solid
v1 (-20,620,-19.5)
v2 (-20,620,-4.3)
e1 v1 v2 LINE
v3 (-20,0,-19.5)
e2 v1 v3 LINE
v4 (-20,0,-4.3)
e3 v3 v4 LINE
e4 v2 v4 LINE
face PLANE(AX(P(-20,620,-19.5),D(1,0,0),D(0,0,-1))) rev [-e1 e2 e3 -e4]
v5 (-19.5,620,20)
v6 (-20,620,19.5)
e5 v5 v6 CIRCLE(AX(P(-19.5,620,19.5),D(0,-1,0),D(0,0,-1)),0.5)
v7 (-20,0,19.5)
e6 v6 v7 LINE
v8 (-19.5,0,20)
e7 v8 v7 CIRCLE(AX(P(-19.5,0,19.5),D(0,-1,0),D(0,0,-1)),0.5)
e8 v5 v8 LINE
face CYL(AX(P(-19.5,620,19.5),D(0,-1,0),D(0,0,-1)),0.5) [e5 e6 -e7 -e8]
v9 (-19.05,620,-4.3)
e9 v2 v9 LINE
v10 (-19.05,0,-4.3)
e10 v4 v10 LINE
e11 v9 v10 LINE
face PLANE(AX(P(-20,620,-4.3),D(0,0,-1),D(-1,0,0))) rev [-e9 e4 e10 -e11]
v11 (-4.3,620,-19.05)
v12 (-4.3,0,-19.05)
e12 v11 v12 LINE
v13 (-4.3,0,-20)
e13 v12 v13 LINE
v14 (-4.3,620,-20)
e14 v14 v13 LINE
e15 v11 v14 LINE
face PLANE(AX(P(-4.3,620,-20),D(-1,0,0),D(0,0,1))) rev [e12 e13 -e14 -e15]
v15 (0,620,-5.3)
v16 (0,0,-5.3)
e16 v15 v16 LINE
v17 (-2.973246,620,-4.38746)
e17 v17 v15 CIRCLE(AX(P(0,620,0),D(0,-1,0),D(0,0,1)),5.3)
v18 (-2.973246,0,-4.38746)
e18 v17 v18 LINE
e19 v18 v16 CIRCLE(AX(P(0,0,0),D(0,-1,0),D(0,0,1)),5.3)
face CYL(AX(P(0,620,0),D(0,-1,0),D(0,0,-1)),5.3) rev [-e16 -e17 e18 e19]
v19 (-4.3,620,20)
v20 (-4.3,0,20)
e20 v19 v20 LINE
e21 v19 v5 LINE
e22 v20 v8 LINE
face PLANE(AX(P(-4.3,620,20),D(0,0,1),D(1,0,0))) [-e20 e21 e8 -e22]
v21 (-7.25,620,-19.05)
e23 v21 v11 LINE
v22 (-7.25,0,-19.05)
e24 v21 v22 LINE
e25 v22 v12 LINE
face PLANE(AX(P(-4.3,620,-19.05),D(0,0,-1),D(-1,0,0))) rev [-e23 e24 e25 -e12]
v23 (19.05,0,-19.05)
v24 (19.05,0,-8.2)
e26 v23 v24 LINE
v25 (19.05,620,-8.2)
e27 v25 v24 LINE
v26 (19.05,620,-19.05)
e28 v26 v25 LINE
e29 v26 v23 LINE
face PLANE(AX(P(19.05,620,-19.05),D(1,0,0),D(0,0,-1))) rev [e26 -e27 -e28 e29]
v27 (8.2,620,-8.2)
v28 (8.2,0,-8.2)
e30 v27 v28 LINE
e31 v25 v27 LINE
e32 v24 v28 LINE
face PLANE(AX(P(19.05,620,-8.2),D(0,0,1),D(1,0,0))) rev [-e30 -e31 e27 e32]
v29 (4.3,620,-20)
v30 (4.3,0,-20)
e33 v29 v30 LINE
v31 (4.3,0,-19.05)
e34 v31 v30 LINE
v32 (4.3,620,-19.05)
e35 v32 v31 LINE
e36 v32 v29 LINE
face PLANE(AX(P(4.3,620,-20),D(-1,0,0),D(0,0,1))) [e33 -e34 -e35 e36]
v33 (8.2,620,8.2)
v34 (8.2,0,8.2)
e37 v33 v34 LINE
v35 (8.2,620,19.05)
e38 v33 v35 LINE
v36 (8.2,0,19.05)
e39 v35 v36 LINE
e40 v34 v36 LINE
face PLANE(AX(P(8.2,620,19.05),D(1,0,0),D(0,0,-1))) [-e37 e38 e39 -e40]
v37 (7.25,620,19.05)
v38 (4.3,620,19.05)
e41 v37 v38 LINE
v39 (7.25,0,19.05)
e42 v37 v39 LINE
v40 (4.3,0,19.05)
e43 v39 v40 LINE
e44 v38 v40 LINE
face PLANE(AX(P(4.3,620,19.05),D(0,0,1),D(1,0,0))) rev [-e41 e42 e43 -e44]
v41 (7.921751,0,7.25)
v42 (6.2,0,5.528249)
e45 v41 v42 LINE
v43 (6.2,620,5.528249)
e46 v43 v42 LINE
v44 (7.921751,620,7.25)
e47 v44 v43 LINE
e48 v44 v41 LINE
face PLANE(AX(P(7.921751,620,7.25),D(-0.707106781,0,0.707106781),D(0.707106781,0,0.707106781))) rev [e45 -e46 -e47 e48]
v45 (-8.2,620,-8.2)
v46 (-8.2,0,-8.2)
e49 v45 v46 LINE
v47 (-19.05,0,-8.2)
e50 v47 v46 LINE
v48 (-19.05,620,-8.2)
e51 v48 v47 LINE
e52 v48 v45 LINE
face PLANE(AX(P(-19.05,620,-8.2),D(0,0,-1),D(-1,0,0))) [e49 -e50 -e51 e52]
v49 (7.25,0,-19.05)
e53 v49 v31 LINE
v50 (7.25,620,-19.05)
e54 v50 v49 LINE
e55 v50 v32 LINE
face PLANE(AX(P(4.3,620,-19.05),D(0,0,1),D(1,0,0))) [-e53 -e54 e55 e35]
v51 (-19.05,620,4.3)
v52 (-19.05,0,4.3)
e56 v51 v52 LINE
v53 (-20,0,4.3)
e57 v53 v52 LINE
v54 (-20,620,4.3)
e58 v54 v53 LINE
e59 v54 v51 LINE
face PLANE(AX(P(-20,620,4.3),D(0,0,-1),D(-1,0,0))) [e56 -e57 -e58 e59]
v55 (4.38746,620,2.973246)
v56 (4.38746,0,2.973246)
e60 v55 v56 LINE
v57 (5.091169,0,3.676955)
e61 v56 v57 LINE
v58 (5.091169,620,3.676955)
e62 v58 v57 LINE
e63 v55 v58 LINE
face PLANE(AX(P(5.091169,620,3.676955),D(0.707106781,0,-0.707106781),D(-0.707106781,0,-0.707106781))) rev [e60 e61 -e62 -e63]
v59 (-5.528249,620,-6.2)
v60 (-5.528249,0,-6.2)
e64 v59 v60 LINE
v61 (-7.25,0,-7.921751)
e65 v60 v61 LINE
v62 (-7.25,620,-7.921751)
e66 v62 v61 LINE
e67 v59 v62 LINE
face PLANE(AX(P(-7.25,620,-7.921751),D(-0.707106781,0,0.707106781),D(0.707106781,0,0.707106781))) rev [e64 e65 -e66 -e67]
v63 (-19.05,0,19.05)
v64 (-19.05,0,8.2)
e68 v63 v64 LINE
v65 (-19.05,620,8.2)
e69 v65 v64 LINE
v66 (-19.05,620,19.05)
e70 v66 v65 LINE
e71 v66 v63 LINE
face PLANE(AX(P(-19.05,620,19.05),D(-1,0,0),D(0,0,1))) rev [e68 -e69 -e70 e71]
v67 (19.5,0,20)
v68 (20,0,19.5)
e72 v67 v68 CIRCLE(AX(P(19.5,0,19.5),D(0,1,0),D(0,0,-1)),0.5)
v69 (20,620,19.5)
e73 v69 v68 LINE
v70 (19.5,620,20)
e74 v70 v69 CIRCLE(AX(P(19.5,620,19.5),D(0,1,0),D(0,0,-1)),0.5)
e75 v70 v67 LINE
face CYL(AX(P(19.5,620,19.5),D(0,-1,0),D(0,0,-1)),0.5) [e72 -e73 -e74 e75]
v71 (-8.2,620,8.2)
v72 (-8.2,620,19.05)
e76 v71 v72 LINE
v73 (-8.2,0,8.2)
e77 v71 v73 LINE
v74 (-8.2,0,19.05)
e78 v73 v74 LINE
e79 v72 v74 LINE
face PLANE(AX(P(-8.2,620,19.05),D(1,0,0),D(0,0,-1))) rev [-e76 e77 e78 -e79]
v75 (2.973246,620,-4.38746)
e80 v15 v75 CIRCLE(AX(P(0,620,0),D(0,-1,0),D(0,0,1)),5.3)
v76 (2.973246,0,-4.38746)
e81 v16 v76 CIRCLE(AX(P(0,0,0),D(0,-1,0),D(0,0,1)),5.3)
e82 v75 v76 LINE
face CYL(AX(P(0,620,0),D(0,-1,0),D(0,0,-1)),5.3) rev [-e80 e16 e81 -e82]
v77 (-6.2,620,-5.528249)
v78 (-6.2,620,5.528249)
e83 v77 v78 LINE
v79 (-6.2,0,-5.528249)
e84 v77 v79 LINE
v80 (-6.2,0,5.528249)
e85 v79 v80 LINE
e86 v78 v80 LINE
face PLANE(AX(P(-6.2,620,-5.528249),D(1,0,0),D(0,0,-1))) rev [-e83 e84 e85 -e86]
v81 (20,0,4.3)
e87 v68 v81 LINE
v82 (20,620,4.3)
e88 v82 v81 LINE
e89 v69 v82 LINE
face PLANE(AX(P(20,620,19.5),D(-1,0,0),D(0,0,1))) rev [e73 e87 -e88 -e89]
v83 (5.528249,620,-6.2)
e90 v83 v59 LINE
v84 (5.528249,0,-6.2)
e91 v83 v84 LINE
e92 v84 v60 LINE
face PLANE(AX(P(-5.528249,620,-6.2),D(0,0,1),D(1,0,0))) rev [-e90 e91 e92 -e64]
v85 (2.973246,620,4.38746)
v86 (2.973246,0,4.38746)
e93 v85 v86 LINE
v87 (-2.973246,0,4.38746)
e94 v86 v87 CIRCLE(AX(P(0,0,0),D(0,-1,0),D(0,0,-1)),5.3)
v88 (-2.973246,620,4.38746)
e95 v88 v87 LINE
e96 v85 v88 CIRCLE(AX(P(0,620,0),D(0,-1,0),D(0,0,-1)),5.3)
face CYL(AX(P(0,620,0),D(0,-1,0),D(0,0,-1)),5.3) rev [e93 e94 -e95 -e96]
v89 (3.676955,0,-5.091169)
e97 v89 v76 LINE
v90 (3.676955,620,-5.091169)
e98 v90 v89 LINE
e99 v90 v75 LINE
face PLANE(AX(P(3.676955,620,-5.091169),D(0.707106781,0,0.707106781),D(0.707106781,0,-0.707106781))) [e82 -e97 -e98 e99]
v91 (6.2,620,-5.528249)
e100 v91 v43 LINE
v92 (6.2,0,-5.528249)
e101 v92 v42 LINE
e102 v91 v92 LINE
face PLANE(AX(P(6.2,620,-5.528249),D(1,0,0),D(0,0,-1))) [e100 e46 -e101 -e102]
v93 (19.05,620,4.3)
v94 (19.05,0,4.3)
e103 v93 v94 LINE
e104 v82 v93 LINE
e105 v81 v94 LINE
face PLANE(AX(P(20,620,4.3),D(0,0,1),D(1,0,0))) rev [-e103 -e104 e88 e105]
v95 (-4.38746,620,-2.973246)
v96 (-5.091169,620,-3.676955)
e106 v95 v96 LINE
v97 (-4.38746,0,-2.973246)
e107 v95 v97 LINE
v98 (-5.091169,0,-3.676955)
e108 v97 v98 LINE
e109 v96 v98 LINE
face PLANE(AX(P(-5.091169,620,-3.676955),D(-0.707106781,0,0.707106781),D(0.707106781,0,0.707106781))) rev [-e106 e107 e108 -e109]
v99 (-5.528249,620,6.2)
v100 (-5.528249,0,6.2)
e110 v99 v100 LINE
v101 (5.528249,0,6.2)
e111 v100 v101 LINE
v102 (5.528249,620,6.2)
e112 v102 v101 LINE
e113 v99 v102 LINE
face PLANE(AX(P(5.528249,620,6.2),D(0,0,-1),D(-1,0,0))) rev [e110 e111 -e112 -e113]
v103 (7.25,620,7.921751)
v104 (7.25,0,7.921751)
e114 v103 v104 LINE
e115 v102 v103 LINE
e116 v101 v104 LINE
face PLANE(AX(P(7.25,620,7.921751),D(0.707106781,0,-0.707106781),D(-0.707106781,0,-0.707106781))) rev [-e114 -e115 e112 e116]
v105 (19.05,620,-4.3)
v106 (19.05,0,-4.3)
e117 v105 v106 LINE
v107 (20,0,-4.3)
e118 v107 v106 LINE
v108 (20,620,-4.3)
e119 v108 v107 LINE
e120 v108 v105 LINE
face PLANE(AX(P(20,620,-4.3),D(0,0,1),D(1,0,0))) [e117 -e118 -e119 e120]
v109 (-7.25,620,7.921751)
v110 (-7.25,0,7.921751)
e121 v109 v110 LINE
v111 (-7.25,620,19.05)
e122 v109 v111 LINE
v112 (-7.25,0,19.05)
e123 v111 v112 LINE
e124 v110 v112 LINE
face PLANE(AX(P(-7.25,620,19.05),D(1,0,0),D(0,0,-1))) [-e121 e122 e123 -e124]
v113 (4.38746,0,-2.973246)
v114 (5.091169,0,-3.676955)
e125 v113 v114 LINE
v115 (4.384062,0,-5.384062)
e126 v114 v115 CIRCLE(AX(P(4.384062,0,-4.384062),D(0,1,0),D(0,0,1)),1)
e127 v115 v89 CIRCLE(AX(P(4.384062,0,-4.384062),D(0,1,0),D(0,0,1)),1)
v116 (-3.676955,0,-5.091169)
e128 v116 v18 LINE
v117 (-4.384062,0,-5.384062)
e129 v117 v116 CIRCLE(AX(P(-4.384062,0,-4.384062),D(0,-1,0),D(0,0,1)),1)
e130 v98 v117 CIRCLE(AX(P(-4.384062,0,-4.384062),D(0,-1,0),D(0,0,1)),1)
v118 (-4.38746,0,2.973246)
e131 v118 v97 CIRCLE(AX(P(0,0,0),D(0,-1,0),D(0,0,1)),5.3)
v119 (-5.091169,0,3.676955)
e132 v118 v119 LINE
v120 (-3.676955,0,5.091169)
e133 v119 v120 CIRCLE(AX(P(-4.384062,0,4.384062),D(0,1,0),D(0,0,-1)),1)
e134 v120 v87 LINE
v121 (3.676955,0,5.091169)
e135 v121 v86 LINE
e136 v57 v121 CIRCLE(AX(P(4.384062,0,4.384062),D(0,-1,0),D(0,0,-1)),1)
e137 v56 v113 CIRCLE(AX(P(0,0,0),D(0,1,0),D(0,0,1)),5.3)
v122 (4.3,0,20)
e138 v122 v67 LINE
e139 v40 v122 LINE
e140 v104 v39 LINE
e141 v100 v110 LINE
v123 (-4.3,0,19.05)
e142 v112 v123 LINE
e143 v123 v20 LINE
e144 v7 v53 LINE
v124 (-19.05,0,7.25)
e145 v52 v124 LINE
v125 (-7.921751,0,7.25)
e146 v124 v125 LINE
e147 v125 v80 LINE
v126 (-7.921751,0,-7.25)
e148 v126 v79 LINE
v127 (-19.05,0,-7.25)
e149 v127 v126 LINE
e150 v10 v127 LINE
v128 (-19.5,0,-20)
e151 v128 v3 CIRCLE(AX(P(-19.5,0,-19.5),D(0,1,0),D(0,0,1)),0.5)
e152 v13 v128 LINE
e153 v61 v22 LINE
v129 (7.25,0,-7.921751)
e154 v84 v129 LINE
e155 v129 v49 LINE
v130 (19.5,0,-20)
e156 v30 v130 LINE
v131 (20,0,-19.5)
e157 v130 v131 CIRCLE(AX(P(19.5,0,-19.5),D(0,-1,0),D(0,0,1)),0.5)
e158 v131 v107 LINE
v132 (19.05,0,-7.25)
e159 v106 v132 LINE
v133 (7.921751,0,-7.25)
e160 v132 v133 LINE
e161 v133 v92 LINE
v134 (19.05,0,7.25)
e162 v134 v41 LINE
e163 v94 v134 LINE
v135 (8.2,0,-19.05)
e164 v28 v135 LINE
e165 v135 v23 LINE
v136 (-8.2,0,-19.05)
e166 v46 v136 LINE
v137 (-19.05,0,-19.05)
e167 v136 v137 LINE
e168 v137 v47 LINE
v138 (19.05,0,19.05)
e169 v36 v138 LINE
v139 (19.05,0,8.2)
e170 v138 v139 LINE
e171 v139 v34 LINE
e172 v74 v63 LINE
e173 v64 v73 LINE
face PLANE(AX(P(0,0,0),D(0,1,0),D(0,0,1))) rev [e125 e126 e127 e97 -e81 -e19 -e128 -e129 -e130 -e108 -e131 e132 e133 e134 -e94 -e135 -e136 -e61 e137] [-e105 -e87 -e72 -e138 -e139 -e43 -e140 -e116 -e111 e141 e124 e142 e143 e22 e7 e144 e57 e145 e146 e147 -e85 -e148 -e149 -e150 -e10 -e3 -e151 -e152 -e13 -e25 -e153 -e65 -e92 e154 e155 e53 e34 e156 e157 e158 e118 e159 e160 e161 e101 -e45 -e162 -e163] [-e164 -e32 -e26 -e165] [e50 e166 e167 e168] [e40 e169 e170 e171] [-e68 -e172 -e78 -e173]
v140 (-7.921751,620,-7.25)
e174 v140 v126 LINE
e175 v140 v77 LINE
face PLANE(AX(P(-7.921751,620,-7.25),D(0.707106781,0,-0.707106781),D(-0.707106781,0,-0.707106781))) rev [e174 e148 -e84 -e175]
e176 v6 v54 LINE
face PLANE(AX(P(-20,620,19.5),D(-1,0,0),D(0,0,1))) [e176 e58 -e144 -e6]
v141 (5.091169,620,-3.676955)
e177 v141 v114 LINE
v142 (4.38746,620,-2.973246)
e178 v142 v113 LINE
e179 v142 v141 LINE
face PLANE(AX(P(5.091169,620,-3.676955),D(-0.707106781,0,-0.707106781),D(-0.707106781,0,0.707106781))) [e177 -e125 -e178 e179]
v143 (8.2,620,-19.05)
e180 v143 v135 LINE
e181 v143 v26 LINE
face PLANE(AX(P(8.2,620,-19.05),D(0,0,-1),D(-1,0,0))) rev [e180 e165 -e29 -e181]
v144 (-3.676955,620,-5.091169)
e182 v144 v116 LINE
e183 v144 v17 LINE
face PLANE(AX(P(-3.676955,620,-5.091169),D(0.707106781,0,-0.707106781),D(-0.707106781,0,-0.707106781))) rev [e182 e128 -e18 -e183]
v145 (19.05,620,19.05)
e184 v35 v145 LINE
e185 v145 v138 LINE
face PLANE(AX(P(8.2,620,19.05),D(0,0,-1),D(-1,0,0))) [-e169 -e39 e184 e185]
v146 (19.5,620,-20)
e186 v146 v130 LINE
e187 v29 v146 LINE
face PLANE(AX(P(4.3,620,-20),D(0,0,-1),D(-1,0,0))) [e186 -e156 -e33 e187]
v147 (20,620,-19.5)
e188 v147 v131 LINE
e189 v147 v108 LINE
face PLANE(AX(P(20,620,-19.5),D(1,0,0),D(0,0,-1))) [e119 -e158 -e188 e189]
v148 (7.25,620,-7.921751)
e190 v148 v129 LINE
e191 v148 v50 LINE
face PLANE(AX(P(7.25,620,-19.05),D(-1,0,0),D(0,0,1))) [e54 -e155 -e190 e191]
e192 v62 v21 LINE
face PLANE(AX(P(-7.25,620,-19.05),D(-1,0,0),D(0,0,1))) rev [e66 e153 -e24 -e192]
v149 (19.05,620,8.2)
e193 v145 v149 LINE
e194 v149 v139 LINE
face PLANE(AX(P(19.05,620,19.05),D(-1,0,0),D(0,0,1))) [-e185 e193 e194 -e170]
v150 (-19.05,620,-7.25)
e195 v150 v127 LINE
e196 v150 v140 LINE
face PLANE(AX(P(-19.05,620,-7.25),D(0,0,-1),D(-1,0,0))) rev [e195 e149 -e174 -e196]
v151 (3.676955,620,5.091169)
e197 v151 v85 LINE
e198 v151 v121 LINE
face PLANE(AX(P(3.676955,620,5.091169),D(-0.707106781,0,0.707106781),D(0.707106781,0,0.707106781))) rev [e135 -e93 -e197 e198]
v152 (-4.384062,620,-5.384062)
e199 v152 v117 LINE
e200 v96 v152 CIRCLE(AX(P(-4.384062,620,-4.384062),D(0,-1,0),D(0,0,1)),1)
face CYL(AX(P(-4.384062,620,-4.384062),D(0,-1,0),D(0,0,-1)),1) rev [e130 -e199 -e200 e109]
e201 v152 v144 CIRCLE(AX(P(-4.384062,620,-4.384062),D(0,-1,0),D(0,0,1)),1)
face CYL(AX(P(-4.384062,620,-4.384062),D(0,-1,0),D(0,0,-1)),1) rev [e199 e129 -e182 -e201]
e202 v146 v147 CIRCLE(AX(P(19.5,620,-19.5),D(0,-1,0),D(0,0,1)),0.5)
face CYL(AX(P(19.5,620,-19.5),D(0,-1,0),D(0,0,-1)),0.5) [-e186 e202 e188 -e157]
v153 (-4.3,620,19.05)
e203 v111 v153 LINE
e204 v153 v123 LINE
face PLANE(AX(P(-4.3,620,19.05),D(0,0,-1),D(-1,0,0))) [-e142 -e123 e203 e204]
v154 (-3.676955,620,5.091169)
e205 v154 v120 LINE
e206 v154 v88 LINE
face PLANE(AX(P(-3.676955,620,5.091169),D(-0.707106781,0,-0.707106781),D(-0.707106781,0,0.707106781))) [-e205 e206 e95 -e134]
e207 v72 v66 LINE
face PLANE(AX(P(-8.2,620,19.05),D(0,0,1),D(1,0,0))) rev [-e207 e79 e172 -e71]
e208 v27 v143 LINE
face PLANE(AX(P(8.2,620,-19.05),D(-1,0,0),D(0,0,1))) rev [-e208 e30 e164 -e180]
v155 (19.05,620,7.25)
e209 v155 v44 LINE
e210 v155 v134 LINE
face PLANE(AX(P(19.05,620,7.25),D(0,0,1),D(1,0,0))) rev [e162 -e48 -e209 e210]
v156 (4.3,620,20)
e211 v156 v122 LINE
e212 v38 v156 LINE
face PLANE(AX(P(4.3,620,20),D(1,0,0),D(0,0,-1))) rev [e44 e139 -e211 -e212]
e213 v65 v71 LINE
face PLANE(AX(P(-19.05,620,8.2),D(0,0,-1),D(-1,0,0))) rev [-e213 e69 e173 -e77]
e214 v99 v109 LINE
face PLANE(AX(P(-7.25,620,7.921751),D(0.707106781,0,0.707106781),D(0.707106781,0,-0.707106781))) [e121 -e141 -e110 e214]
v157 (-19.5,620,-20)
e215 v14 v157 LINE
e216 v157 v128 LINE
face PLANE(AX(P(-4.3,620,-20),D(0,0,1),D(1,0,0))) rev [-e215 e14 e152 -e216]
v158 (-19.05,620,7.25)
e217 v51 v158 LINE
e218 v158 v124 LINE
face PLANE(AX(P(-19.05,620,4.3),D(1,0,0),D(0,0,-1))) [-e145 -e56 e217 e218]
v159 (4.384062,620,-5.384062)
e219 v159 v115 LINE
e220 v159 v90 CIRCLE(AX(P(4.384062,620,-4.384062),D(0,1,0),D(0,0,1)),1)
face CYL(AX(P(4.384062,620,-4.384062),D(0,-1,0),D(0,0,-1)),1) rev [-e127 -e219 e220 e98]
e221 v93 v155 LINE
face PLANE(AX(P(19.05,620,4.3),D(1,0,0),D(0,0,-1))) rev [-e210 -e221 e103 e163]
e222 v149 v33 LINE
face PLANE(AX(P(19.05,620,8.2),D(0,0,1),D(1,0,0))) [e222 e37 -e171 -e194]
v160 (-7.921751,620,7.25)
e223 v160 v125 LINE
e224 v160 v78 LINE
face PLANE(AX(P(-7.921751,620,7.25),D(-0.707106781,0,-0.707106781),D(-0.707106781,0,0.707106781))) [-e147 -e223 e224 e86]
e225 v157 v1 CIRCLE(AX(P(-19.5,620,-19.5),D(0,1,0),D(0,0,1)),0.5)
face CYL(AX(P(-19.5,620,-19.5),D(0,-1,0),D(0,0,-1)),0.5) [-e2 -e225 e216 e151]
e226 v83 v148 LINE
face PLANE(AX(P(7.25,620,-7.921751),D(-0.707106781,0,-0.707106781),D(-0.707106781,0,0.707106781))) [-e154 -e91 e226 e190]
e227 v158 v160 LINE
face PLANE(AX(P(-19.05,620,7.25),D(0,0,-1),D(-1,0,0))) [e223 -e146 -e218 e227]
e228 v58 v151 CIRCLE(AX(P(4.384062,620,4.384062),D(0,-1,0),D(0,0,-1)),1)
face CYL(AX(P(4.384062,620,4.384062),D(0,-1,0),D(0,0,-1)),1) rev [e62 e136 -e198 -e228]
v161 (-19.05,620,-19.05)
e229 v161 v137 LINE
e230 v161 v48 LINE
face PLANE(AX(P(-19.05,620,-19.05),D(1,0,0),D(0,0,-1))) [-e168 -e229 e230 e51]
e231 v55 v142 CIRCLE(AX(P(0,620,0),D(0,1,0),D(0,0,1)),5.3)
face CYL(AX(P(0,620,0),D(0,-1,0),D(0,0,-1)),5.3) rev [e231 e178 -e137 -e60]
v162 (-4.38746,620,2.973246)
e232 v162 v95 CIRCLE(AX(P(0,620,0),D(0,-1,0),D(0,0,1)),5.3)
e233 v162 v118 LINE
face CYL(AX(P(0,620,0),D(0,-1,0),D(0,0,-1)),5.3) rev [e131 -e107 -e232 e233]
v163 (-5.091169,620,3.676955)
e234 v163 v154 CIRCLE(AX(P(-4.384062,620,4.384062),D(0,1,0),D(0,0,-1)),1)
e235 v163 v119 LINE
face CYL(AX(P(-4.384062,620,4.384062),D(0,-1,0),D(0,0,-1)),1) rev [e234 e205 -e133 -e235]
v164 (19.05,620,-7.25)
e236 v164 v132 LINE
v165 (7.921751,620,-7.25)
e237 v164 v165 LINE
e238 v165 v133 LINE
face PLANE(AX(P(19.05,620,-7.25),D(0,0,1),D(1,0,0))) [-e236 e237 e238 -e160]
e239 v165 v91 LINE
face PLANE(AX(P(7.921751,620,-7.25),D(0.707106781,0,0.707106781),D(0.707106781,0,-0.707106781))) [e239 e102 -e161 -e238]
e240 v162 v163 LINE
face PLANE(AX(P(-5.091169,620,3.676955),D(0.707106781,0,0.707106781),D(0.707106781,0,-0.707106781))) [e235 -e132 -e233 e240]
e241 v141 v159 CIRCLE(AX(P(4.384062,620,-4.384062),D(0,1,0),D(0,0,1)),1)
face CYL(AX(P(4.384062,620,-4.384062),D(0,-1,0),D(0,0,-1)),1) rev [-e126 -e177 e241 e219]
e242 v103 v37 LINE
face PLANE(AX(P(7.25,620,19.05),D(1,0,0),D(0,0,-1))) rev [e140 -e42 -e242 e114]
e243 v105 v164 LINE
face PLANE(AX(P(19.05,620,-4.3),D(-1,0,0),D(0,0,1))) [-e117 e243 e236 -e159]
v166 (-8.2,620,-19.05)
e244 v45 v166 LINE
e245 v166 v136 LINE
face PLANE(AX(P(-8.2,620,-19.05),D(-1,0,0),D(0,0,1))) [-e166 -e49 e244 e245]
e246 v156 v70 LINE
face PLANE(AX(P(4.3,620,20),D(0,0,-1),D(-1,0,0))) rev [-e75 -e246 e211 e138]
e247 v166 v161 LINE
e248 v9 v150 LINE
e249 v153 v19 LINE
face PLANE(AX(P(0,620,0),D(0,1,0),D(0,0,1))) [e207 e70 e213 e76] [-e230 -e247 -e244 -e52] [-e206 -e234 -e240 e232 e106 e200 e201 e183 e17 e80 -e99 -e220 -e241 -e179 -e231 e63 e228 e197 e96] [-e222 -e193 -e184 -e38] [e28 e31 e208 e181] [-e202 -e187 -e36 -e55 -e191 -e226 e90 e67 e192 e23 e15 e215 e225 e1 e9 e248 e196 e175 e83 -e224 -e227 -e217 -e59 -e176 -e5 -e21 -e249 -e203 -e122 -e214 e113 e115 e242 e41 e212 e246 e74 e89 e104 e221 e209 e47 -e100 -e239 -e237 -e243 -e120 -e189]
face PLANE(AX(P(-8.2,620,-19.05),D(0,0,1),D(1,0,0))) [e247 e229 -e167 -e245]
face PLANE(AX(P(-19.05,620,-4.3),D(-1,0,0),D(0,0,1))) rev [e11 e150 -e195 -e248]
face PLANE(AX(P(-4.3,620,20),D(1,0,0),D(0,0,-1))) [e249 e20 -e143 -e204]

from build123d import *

# Parameters (mm, degrees)
SKETCH1_W               = 10.85
SKETCH1_H               = 10.85
BOSS_EXTRUDE1_DEPTH     = 620
MIRROR2_COPY_1_SKETCH_W = 10.85
MIRROR2_COPY_1_SKETCH_H = 10.85
MIRROR2_COPY_1_DEPTH    = 620


with BuildPart() as part:
    # Sketch1 → Boss-Extrude1 (new body)
    with BuildSketch(Plane(origin=(0, 0, 0), x_dir=(1, 0, 0), z_dir=(0, 1, 0))):
        with BuildLine():
            Line((-4.3, 20), (-19.5, 20))
            ThreePointArc((-19.5, 20), (-19.853553391, 19.853553391), (-20, 19.5))
            Line((-20, 19.5), (-20, 4.3))
            Line((-20, 4.3), (-19.05, 4.3))
            Line((-19.05, 4.3), (-19.05, 7.25))
            Line((-19.05, 7.25), (-7.921751442, 7.25))
            Line((-7.921751442, 7.25), (-6.2, 5.528248558))
            Line((-6.2, 5.528248558), (-6.2, 0))
            Line((-6.2, 0), (-5.3, 0))
            ThreePointArc((-5.3, 0), (-5.066731596, 1.555066215), (-4.387460025, 2.973246463))
            Line((-4.387460025, 2.973246463), (-5.091168825, 3.676955262))
            ThreePointArc((-5.091168825, 3.676955262), (-5.091168825, 5.091168825), (-3.676955262, 5.091168825))
            Line((-3.676955262, 5.091168825), (-2.973246463, 4.387460025))
            ThreePointArc((-2.973246463, 4.387460025), (-1.555066215, 5.066731596), (0, 5.3))
            Line((0, 5.3), (0, 6.2))
            Line((0, 6.2), (-5.528248558, 6.2))
            Line((-5.528248558, 6.2), (-7.25, 7.921751442))
            Line((-7.25, 7.921751442), (-7.25, 19.05))
            Line((-7.25, 19.05), (-4.3, 19.05))
            Line((-4.3, 19.05), (-4.3, 20))
        make_face()
        with Locations((-13.625, 13.625)):
            Rectangle(SKETCH1_W, SKETCH1_H, mode=Mode.SUBTRACT)
    boss_extrude1 = extrude(amount=BOSS_EXTRUDE1_DEPTH)

    # Mirror1: Boss-Extrude1 across plane
    add(boss_extrude1.mirror(Plane(origin=(0, 0, 0), x_dir=(0, 0, 1), z_dir=(1, 0, 0))))

    # Mirror2: Boss-Extrude1 across plane
    add(boss_extrude1.mirror(Plane.XY))

    # Mirror2 copy 1 sketch → Mirror2 copy 1 (add)
    with BuildSketch(Plane(origin=(0, 0, 0), x_dir=(-1, 0, 0), z_dir=(0, 1, 0))):
        with BuildLine():
            Line((-4.3, 20), (-19.5, 20))
            ThreePointArc((-19.5, 20), (-19.853553391, 19.853553391), (-20, 19.5))
            Line((-20, 19.5), (-20, 4.3))
            Line((-20, 4.3), (-19.05, 4.3))
            Line((-19.05, 4.3), (-19.05, 7.25))
            Line((-19.05, 7.25), (-7.921751442, 7.25))
            Line((-7.921751442, 7.25), (-6.2, 5.528248558))
            Line((-6.2, 5.528248558), (-6.2, 0))
            Line((-6.2, 0), (-5.3, 0))
            ThreePointArc((-5.3, 0), (-5.066731596, 1.555066215), (-4.387460025, 2.973246463))
            Line((-4.387460025, 2.973246463), (-5.091168825, 3.676955262))
            ThreePointArc((-5.091168825, 3.676955262), (-5.091168825, 5.091168825), (-3.676955262, 5.091168825))
            Line((-3.676955262, 5.091168825), (-2.973246463, 4.387460025))
            ThreePointArc((-2.973246463, 4.387460025), (-1.555066215, 5.066731596), (0, 5.3))
            Line((0, 5.3), (0, 6.2))
            Line((0, 6.2), (-5.528248558, 6.2))
            Line((-5.528248558, 6.2), (-7.25, 7.921751442))
            Line((-7.25, 7.921751442), (-7.25, 19.05))
            Line((-7.25, 19.05), (-4.3, 19.05))
            Line((-4.3, 19.05), (-4.3, 20))
        make_face()
        with Locations((-13.625, 13.625)):
            Rectangle(MIRROR2_COPY_1_SKETCH_W, MIRROR2_COPY_1_SKETCH_H, mode=Mode.SUBTRACT)
    extrude(amount=MIRROR2_COPY_1_DEPTH)


solid = part.part
